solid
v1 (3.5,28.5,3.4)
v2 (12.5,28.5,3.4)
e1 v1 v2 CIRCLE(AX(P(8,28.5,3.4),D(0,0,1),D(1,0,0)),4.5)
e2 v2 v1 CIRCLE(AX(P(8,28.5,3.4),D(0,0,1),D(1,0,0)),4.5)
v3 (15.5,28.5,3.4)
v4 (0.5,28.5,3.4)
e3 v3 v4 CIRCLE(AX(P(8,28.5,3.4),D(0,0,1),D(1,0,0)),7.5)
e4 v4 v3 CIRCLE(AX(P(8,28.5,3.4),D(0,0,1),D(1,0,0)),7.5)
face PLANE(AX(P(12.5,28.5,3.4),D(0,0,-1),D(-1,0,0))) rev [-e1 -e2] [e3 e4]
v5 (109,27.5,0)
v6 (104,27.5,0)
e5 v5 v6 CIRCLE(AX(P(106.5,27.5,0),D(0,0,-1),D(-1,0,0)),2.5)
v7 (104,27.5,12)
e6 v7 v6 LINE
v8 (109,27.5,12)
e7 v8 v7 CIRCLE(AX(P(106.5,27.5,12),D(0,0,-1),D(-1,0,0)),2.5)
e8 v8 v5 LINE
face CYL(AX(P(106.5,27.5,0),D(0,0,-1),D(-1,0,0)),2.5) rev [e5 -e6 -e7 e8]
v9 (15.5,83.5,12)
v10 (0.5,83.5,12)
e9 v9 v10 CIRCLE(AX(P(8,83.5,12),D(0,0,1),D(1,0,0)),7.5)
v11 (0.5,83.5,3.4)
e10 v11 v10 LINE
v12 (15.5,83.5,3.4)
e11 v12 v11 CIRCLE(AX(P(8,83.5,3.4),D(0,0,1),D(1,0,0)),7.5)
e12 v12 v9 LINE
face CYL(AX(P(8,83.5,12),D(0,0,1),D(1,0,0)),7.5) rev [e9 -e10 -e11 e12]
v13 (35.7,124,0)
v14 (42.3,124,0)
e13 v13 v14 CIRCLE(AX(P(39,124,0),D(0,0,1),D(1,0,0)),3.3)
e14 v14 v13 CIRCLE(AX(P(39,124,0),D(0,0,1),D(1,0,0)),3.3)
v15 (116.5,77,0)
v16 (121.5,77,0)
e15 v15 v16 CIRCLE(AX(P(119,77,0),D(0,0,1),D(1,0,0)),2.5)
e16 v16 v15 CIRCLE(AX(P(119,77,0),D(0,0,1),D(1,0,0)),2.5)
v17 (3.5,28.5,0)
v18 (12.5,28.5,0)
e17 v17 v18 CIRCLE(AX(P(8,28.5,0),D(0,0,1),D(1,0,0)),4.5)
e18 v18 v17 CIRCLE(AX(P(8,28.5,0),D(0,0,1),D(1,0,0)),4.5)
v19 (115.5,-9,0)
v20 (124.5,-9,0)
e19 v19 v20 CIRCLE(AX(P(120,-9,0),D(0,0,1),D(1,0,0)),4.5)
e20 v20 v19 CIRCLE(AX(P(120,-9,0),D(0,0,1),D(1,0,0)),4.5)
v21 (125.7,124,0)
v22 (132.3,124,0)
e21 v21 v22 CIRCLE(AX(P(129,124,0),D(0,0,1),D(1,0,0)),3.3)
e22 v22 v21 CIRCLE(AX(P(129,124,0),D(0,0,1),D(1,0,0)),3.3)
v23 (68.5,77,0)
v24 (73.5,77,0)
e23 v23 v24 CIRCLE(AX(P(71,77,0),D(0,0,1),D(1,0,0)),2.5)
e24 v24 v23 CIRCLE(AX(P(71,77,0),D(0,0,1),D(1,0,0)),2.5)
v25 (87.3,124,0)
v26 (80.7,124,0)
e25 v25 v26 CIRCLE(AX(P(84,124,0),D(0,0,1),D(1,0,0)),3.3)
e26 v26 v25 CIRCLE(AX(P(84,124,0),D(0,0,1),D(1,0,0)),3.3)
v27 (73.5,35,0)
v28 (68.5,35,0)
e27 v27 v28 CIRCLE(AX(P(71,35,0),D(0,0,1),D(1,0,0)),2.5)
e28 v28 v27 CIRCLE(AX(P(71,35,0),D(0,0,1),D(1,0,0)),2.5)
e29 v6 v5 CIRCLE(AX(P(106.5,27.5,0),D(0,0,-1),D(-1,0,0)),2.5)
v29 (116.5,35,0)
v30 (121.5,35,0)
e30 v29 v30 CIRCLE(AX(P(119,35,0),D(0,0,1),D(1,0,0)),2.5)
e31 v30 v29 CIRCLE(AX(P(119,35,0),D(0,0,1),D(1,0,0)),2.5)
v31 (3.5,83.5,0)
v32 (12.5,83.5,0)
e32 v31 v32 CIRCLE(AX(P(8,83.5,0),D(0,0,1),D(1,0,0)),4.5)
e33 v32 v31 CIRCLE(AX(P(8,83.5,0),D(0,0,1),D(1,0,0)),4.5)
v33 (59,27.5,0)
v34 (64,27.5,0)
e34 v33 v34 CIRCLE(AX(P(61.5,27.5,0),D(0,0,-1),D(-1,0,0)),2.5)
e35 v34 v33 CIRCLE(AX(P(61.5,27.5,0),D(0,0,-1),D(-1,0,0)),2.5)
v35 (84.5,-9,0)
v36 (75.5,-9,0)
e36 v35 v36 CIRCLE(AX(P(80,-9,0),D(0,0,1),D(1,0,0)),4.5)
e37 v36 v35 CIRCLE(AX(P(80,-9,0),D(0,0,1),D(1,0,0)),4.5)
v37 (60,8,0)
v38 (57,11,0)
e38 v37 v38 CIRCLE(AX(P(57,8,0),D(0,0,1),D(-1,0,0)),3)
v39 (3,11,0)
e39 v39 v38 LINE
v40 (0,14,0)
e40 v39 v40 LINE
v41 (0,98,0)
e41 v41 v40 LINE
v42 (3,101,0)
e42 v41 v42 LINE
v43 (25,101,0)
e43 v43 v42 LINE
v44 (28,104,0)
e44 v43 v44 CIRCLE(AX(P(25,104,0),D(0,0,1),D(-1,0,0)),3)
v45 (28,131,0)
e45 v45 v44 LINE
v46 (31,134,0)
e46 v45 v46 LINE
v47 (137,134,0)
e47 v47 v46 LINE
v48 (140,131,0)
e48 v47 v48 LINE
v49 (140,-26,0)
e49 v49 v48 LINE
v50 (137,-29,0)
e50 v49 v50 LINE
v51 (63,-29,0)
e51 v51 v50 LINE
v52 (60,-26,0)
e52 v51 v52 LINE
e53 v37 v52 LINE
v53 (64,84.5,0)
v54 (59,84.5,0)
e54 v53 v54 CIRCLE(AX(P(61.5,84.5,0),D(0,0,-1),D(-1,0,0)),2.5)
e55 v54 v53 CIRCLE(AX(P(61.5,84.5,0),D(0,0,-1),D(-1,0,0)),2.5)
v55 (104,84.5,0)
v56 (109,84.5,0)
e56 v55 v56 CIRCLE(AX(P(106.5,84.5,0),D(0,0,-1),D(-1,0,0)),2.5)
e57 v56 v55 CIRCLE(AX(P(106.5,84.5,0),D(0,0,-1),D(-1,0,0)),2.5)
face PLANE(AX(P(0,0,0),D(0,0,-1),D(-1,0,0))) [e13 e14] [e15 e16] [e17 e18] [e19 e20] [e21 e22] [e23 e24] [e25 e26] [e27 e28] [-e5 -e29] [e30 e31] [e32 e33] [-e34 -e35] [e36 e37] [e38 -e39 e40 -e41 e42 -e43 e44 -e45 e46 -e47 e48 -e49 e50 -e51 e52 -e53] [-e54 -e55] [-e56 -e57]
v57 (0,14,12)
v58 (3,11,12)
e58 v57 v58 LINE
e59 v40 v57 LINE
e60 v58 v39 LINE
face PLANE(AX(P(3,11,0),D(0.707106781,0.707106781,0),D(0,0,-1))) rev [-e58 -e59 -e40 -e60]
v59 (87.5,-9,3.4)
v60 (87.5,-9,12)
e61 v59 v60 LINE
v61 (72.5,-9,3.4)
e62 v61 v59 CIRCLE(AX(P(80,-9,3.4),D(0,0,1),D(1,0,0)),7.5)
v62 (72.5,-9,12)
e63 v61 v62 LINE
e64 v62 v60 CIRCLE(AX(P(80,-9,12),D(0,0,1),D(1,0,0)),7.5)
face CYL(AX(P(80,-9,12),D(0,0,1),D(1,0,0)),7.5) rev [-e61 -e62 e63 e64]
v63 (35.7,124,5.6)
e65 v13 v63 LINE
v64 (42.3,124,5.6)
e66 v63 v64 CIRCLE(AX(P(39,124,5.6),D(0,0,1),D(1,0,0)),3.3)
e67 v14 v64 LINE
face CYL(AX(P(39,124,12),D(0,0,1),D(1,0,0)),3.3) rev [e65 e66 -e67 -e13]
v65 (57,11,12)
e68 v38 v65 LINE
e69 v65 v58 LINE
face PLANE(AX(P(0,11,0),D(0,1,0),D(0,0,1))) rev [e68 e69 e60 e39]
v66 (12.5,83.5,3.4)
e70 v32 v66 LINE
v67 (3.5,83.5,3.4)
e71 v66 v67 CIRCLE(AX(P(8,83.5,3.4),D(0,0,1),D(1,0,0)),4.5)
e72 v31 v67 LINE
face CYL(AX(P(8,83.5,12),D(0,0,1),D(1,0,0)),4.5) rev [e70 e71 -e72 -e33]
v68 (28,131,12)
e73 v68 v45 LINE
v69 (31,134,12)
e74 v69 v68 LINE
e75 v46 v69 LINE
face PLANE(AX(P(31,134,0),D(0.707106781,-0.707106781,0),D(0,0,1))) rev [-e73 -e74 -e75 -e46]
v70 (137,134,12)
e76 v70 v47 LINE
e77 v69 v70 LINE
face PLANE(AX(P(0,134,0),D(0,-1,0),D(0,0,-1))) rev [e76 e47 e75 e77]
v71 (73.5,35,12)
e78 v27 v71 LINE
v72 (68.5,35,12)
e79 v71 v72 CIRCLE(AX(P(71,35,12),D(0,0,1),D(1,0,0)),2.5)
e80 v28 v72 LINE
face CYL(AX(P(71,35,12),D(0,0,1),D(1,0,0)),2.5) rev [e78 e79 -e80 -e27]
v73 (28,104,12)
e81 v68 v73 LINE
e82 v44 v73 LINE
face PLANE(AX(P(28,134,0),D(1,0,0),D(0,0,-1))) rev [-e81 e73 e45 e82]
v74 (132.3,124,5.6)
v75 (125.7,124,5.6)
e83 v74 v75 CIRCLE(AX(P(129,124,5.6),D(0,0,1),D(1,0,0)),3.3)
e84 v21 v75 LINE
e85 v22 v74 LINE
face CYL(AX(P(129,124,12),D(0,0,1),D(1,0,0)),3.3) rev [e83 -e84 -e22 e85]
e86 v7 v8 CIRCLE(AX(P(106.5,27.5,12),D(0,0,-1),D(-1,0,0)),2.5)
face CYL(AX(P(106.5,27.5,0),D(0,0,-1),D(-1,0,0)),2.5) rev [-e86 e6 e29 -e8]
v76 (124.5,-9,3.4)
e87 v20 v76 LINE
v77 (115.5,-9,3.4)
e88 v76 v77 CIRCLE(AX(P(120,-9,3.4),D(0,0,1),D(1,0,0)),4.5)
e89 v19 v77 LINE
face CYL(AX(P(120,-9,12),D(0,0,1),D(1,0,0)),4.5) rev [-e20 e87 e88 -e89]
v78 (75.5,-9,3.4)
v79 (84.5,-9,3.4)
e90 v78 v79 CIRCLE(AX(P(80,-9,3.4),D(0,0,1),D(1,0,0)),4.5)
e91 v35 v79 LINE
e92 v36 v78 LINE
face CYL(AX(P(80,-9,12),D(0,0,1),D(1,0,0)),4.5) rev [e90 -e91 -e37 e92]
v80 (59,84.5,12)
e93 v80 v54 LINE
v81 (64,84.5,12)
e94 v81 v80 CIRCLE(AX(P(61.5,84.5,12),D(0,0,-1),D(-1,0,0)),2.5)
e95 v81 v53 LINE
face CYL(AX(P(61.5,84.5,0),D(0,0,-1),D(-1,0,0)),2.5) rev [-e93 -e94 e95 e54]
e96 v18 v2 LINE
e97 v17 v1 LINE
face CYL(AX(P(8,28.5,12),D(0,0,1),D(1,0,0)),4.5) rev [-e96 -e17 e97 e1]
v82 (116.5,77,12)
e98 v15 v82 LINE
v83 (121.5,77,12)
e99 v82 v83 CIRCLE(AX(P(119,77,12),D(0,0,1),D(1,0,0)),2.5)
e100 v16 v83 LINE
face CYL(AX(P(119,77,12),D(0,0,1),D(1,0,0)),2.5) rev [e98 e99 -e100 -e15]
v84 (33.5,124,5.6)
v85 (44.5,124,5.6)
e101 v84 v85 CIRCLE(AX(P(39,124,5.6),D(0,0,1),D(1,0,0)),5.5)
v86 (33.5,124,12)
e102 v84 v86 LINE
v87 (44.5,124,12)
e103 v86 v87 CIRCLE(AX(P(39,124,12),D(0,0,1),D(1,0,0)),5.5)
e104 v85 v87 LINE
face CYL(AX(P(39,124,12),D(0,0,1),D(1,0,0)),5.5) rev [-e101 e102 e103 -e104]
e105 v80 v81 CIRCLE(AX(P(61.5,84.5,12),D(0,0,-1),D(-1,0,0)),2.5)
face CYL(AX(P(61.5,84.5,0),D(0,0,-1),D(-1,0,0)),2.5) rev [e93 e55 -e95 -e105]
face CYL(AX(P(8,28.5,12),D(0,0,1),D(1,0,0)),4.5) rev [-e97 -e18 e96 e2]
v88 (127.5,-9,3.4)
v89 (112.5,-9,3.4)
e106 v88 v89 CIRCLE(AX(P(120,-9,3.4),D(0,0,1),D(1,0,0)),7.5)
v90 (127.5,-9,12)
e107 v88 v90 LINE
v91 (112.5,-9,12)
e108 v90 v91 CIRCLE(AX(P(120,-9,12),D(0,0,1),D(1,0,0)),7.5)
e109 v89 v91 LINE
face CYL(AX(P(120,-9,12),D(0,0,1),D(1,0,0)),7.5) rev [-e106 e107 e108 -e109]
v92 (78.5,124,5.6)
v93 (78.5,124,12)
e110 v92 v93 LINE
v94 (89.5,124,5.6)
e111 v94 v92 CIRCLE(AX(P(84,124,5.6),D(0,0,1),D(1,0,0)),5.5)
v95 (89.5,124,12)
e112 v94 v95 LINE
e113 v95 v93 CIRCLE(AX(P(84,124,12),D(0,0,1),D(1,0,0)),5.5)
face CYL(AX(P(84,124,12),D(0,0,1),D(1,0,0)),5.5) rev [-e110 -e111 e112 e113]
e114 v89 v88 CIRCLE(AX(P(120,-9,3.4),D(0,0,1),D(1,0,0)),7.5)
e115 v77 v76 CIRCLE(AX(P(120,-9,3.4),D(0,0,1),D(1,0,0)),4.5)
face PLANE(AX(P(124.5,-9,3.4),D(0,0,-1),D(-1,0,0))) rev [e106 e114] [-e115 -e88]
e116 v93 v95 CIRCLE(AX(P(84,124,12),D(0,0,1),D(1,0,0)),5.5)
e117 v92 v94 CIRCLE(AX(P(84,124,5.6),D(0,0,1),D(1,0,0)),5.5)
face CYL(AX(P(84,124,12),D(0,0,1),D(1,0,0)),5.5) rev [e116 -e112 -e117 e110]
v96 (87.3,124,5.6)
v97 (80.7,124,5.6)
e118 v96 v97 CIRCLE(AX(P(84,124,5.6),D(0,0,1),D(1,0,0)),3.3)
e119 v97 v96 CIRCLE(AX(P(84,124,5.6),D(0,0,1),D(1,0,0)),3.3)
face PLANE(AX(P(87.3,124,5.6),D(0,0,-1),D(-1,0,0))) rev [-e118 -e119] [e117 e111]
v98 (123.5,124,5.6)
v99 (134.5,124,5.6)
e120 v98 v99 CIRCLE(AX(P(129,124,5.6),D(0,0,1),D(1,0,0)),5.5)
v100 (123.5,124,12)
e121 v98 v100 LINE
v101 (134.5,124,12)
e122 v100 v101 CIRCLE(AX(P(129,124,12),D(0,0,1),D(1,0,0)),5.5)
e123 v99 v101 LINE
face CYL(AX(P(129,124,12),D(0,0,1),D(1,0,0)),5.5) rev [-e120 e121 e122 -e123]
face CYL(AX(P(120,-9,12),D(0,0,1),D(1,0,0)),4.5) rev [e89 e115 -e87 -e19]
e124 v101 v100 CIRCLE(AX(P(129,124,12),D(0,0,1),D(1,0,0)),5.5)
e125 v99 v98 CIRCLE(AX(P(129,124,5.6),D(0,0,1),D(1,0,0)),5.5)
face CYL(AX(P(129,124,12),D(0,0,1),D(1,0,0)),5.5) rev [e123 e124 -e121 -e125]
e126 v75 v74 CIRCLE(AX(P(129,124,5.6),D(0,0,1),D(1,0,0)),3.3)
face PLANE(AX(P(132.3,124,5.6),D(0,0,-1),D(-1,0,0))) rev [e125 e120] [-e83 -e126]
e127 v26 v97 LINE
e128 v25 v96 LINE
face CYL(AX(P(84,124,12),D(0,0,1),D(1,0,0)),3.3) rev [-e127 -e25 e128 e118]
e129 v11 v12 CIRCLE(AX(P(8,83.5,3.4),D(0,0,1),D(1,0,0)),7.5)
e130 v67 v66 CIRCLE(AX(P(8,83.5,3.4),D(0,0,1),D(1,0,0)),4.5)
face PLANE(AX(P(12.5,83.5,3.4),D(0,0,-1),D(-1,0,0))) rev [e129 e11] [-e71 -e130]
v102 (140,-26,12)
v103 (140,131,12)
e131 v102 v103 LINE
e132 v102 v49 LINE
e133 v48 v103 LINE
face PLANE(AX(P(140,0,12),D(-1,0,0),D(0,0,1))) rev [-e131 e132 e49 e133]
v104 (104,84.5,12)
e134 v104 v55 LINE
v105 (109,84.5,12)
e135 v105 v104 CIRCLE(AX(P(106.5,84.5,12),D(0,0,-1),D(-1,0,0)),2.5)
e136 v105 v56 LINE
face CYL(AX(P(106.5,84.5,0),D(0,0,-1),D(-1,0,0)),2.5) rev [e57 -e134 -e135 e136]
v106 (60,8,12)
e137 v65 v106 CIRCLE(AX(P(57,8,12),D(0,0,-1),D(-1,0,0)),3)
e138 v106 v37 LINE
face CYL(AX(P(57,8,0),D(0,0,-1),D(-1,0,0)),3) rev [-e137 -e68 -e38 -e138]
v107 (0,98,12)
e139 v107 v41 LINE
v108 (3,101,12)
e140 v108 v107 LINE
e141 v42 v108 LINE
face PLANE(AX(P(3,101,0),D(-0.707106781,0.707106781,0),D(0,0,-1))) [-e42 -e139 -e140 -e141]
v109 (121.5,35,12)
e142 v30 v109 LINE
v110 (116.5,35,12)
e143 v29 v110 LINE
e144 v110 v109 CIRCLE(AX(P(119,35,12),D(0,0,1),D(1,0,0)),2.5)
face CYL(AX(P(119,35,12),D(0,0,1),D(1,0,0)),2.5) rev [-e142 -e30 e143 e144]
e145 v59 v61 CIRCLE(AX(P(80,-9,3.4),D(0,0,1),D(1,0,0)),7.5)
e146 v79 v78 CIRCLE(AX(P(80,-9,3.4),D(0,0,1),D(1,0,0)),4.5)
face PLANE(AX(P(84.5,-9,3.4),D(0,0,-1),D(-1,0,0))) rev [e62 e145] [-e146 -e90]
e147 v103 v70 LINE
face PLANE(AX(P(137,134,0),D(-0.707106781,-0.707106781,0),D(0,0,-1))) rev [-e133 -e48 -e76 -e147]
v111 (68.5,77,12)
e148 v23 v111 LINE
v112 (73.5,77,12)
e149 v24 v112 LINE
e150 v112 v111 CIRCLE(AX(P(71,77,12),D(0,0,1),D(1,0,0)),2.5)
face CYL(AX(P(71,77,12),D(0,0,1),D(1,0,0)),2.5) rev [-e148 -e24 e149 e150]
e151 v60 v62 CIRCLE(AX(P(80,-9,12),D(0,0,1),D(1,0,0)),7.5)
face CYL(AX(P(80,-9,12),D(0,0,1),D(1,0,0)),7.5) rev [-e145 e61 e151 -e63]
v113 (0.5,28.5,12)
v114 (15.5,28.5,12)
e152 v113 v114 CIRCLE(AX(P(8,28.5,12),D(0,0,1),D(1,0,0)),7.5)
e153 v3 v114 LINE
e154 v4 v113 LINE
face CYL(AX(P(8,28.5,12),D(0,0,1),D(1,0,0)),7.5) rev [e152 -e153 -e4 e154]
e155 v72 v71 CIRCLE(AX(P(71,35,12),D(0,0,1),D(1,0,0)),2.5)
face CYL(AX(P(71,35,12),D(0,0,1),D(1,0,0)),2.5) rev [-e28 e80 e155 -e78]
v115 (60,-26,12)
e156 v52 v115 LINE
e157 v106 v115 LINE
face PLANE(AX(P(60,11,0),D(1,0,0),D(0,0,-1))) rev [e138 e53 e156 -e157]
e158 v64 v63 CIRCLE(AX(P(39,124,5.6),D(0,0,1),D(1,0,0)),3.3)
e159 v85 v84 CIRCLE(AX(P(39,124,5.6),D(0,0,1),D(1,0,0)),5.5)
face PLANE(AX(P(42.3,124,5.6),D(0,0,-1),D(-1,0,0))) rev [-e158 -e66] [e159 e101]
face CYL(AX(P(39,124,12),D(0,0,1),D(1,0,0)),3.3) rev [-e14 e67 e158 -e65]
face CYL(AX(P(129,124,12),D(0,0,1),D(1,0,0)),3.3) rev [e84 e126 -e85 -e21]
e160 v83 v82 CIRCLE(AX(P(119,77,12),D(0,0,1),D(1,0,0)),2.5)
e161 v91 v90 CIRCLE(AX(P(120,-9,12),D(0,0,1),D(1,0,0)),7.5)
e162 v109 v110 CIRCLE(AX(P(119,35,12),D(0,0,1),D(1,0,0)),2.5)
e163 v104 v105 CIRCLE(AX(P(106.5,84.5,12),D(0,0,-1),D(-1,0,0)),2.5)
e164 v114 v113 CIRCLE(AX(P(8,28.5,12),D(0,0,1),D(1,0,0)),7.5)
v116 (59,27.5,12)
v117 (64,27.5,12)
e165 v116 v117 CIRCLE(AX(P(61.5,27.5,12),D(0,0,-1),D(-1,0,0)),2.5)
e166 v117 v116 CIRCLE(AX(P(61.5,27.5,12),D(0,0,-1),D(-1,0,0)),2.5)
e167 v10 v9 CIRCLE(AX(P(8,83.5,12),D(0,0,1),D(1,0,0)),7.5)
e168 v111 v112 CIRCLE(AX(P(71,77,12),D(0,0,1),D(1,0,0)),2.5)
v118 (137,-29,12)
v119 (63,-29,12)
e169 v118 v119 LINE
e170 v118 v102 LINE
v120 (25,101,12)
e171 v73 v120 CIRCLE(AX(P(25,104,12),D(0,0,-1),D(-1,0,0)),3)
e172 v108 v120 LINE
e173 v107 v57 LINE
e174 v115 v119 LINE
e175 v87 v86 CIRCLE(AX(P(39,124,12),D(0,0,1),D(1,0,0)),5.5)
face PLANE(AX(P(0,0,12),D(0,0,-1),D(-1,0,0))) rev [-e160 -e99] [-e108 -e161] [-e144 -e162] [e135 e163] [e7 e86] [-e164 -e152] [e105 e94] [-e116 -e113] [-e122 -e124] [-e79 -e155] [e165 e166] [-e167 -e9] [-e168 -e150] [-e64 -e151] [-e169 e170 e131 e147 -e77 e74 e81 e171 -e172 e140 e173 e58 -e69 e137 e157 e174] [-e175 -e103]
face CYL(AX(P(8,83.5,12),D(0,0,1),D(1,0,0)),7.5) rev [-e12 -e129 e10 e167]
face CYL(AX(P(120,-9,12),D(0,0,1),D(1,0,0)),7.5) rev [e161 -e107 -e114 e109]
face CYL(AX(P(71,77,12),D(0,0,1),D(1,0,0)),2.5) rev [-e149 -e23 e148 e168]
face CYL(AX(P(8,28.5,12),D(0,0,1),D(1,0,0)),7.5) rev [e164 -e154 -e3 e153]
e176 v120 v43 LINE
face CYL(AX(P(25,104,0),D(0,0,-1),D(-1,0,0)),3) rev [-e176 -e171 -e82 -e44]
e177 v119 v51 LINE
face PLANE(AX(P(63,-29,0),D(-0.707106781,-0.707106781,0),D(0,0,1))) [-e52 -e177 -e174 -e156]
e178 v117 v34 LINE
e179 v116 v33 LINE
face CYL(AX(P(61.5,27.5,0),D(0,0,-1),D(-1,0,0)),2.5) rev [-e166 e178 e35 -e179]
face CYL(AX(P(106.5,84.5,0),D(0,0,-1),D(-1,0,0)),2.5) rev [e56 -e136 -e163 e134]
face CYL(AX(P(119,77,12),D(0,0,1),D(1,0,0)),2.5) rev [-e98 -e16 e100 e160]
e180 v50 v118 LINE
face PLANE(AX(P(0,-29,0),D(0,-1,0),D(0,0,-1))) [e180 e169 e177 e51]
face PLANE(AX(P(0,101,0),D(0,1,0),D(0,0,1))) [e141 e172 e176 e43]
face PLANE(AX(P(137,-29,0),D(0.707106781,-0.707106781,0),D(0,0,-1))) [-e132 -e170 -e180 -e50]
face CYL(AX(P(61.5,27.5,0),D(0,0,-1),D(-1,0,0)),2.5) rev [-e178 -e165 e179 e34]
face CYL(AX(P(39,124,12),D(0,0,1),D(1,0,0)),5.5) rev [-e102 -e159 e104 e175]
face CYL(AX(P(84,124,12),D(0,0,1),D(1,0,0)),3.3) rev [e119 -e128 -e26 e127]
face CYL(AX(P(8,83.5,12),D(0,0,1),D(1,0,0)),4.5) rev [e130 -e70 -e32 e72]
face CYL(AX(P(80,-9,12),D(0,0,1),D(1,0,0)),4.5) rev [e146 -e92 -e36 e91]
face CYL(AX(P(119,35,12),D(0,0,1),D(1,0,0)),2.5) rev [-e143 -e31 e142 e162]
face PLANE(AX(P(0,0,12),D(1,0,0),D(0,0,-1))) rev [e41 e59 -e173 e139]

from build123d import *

# Parameters (mm, degrees)
SKETCH_1_W                     = 140
SKETCH_1_H                     = 112
EXTRUDE_1_DEPTH                = 12
HOLE_WIZARD_M6_1_D             = 5
HOLE_WIZARD_M6_2_D             = 5
SKETCH_6_W                     = 112
SKETCH_6_H                     = 12
EXTRUDE_2_DEPTH                = 22
SKETCH_7_W                     = 28
SKETCH_7_H                     = 12
CUT_EXTRUDE_1_DEPTH            = 11
SKETCH_8_W                     = 60
SKETCH_8_H                     = 12
CUT_EXTRUDE_2_DEPTH            = 11
HOLE_WIZARD_M6_1_2_D           = 6.6
HOLE_WIZARD_M6_1_2_CBORE_D     = 11
HOLE_WIZARD_M6_1_2_CBORE_DEPTH = 6.4
SKETCH_11_W                    = 80
SKETCH_11_H                    = 12
EXTRUDE_3_DEPTH                = 29
CHAMFER_1_SIZE                 = 3
FILLET_1_R                     = 3
HOLE_WIZARD_M8_1_D             = 9
HOLE_WIZARD_M8_1_CBORE_D       = 15
HOLE_WIZARD_M8_1_CBORE_DEPTH   = 8.6
HOLE_WIZARD_M8_2_D             = 9
HOLE_WIZARD_M8_2_CBORE_D       = 15
HOLE_WIZARD_M8_2_CBORE_DEPTH   = 8.6


with BuildPart() as part:
    # 草图1 → 凸台-拉伸1 (new body)
    with BuildSketch(Plane.XY):
        with Locations((70, 56)):
            Rectangle(SKETCH_1_W, SKETCH_1_H)
    extrude(amount=EXTRUDE_1_DEPTH)

    # Hole Wizard M6 _1 (through all)
    with Locations(Plane(origin=(0, 0, 0), x_dir=(-1, 0, 0), z_dir=(0, 0, -1))):
        with Locations((-106.5, 84.5), (-61.5, 84.5), (-61.5, 27.5), (-106.5, 27.5)):
            Hole(HOLE_WIZARD_M6_1_D / 2)

    # M6 螺纹孔2 (through all)
    with Locations(Plane.XY.offset(12)):
        with Locations((71, 77), (71, 35), (119, 35), (119, 77)):
            Hole(HOLE_WIZARD_M6_2_D / 2)

    # 草图6 → 凸台-拉伸2 (add)
    with BuildSketch(Plane(origin=(0, 112, 0), x_dir=(1, 0, 0), z_dir=(0, 1, 0))):
        with Locations((84, -6)):
            Rectangle(SKETCH_6_W, SKETCH_6_H)
    extrude(amount=EXTRUDE_2_DEPTH)

    # 草图7 → 切除-拉伸1 (cut)
    with BuildSketch(Plane(origin=(0, 112, 0), x_dir=(1, 0, 0), z_dir=(0, 1, 0))):
        with Locations((14, -6)):
            Rectangle(SKETCH_7_W, SKETCH_7_H)
    extrude(amount=-CUT_EXTRUDE_1_DEPTH, mode=Mode.SUBTRACT)

    # 草图8 → 切除-拉伸2 (cut)
    with BuildSketch(Plane.XZ):
        with Locations((30, 6)):
            Rectangle(SKETCH_8_W, SKETCH_8_H)
    extrude(amount=-CUT_EXTRUDE_2_DEPTH, mode=Mode.SUBTRACT)

    # Hole Wizard M6 _1 2 (through all)
    with Locations(Plane.XY.offset(12)):
        with Locations((129, 124), (84, 124), (39, 124)):
            CounterBoreHole(HOLE_WIZARD_M6_1_2_D / 2, HOLE_WIZARD_M6_1_2_CBORE_D / 2, HOLE_WIZARD_M6_1_2_CBORE_DEPTH)

    # 草图11 → 凸台-拉伸3 (add)
    with BuildSketch(Plane.XZ):
        with Locations((100, 6)):
            Rectangle(SKETCH_11_W, SKETCH_11_H)
    extrude(amount=EXTRUDE_3_DEPTH)

    # 倒角1
    chamfer_1_edges = [part.edges().sort_by_distance(p)[0] for p in [
        (140, -29, 6),
        (60, -29, 6),
        (0, 11, 6),
        (140, 134, 6),
        (0, 101, 6),
        (28, 134, 6),
    ]]
    chamfer(chamfer_1_edges, length=CHAMFER_1_SIZE)

    # 圆角1
    fillet_1_edges = [part.edges().sort_by_distance(p)[0] for p in [
        (28, 101, 6),
        (60, 11, 6),
    ]]
    fillet(fillet_1_edges, radius=FILLET_1_R)

    # M8 六角凹头螺钉的柱形沉头孔1 (through all)
    with Locations(Plane.XY.offset(12)):
        with Locations((8, 83.5), (8, 28.5)):
            CounterBoreHole(HOLE_WIZARD_M8_1_D / 2, HOLE_WIZARD_M8_1_CBORE_D / 2, HOLE_WIZARD_M8_1_CBORE_DEPTH)

    # M8 六角凹头螺钉的柱形沉头孔2 (through all)
    with Locations(Plane.XY.offset(12)):
        with Locations((80, -9), (120, -9)):
            CounterBoreHole(HOLE_WIZARD_M8_2_D / 2, HOLE_WIZARD_M8_2_CBORE_D / 2, HOLE_WIZARD_M8_2_CBORE_DEPTH)


solid = part.part
